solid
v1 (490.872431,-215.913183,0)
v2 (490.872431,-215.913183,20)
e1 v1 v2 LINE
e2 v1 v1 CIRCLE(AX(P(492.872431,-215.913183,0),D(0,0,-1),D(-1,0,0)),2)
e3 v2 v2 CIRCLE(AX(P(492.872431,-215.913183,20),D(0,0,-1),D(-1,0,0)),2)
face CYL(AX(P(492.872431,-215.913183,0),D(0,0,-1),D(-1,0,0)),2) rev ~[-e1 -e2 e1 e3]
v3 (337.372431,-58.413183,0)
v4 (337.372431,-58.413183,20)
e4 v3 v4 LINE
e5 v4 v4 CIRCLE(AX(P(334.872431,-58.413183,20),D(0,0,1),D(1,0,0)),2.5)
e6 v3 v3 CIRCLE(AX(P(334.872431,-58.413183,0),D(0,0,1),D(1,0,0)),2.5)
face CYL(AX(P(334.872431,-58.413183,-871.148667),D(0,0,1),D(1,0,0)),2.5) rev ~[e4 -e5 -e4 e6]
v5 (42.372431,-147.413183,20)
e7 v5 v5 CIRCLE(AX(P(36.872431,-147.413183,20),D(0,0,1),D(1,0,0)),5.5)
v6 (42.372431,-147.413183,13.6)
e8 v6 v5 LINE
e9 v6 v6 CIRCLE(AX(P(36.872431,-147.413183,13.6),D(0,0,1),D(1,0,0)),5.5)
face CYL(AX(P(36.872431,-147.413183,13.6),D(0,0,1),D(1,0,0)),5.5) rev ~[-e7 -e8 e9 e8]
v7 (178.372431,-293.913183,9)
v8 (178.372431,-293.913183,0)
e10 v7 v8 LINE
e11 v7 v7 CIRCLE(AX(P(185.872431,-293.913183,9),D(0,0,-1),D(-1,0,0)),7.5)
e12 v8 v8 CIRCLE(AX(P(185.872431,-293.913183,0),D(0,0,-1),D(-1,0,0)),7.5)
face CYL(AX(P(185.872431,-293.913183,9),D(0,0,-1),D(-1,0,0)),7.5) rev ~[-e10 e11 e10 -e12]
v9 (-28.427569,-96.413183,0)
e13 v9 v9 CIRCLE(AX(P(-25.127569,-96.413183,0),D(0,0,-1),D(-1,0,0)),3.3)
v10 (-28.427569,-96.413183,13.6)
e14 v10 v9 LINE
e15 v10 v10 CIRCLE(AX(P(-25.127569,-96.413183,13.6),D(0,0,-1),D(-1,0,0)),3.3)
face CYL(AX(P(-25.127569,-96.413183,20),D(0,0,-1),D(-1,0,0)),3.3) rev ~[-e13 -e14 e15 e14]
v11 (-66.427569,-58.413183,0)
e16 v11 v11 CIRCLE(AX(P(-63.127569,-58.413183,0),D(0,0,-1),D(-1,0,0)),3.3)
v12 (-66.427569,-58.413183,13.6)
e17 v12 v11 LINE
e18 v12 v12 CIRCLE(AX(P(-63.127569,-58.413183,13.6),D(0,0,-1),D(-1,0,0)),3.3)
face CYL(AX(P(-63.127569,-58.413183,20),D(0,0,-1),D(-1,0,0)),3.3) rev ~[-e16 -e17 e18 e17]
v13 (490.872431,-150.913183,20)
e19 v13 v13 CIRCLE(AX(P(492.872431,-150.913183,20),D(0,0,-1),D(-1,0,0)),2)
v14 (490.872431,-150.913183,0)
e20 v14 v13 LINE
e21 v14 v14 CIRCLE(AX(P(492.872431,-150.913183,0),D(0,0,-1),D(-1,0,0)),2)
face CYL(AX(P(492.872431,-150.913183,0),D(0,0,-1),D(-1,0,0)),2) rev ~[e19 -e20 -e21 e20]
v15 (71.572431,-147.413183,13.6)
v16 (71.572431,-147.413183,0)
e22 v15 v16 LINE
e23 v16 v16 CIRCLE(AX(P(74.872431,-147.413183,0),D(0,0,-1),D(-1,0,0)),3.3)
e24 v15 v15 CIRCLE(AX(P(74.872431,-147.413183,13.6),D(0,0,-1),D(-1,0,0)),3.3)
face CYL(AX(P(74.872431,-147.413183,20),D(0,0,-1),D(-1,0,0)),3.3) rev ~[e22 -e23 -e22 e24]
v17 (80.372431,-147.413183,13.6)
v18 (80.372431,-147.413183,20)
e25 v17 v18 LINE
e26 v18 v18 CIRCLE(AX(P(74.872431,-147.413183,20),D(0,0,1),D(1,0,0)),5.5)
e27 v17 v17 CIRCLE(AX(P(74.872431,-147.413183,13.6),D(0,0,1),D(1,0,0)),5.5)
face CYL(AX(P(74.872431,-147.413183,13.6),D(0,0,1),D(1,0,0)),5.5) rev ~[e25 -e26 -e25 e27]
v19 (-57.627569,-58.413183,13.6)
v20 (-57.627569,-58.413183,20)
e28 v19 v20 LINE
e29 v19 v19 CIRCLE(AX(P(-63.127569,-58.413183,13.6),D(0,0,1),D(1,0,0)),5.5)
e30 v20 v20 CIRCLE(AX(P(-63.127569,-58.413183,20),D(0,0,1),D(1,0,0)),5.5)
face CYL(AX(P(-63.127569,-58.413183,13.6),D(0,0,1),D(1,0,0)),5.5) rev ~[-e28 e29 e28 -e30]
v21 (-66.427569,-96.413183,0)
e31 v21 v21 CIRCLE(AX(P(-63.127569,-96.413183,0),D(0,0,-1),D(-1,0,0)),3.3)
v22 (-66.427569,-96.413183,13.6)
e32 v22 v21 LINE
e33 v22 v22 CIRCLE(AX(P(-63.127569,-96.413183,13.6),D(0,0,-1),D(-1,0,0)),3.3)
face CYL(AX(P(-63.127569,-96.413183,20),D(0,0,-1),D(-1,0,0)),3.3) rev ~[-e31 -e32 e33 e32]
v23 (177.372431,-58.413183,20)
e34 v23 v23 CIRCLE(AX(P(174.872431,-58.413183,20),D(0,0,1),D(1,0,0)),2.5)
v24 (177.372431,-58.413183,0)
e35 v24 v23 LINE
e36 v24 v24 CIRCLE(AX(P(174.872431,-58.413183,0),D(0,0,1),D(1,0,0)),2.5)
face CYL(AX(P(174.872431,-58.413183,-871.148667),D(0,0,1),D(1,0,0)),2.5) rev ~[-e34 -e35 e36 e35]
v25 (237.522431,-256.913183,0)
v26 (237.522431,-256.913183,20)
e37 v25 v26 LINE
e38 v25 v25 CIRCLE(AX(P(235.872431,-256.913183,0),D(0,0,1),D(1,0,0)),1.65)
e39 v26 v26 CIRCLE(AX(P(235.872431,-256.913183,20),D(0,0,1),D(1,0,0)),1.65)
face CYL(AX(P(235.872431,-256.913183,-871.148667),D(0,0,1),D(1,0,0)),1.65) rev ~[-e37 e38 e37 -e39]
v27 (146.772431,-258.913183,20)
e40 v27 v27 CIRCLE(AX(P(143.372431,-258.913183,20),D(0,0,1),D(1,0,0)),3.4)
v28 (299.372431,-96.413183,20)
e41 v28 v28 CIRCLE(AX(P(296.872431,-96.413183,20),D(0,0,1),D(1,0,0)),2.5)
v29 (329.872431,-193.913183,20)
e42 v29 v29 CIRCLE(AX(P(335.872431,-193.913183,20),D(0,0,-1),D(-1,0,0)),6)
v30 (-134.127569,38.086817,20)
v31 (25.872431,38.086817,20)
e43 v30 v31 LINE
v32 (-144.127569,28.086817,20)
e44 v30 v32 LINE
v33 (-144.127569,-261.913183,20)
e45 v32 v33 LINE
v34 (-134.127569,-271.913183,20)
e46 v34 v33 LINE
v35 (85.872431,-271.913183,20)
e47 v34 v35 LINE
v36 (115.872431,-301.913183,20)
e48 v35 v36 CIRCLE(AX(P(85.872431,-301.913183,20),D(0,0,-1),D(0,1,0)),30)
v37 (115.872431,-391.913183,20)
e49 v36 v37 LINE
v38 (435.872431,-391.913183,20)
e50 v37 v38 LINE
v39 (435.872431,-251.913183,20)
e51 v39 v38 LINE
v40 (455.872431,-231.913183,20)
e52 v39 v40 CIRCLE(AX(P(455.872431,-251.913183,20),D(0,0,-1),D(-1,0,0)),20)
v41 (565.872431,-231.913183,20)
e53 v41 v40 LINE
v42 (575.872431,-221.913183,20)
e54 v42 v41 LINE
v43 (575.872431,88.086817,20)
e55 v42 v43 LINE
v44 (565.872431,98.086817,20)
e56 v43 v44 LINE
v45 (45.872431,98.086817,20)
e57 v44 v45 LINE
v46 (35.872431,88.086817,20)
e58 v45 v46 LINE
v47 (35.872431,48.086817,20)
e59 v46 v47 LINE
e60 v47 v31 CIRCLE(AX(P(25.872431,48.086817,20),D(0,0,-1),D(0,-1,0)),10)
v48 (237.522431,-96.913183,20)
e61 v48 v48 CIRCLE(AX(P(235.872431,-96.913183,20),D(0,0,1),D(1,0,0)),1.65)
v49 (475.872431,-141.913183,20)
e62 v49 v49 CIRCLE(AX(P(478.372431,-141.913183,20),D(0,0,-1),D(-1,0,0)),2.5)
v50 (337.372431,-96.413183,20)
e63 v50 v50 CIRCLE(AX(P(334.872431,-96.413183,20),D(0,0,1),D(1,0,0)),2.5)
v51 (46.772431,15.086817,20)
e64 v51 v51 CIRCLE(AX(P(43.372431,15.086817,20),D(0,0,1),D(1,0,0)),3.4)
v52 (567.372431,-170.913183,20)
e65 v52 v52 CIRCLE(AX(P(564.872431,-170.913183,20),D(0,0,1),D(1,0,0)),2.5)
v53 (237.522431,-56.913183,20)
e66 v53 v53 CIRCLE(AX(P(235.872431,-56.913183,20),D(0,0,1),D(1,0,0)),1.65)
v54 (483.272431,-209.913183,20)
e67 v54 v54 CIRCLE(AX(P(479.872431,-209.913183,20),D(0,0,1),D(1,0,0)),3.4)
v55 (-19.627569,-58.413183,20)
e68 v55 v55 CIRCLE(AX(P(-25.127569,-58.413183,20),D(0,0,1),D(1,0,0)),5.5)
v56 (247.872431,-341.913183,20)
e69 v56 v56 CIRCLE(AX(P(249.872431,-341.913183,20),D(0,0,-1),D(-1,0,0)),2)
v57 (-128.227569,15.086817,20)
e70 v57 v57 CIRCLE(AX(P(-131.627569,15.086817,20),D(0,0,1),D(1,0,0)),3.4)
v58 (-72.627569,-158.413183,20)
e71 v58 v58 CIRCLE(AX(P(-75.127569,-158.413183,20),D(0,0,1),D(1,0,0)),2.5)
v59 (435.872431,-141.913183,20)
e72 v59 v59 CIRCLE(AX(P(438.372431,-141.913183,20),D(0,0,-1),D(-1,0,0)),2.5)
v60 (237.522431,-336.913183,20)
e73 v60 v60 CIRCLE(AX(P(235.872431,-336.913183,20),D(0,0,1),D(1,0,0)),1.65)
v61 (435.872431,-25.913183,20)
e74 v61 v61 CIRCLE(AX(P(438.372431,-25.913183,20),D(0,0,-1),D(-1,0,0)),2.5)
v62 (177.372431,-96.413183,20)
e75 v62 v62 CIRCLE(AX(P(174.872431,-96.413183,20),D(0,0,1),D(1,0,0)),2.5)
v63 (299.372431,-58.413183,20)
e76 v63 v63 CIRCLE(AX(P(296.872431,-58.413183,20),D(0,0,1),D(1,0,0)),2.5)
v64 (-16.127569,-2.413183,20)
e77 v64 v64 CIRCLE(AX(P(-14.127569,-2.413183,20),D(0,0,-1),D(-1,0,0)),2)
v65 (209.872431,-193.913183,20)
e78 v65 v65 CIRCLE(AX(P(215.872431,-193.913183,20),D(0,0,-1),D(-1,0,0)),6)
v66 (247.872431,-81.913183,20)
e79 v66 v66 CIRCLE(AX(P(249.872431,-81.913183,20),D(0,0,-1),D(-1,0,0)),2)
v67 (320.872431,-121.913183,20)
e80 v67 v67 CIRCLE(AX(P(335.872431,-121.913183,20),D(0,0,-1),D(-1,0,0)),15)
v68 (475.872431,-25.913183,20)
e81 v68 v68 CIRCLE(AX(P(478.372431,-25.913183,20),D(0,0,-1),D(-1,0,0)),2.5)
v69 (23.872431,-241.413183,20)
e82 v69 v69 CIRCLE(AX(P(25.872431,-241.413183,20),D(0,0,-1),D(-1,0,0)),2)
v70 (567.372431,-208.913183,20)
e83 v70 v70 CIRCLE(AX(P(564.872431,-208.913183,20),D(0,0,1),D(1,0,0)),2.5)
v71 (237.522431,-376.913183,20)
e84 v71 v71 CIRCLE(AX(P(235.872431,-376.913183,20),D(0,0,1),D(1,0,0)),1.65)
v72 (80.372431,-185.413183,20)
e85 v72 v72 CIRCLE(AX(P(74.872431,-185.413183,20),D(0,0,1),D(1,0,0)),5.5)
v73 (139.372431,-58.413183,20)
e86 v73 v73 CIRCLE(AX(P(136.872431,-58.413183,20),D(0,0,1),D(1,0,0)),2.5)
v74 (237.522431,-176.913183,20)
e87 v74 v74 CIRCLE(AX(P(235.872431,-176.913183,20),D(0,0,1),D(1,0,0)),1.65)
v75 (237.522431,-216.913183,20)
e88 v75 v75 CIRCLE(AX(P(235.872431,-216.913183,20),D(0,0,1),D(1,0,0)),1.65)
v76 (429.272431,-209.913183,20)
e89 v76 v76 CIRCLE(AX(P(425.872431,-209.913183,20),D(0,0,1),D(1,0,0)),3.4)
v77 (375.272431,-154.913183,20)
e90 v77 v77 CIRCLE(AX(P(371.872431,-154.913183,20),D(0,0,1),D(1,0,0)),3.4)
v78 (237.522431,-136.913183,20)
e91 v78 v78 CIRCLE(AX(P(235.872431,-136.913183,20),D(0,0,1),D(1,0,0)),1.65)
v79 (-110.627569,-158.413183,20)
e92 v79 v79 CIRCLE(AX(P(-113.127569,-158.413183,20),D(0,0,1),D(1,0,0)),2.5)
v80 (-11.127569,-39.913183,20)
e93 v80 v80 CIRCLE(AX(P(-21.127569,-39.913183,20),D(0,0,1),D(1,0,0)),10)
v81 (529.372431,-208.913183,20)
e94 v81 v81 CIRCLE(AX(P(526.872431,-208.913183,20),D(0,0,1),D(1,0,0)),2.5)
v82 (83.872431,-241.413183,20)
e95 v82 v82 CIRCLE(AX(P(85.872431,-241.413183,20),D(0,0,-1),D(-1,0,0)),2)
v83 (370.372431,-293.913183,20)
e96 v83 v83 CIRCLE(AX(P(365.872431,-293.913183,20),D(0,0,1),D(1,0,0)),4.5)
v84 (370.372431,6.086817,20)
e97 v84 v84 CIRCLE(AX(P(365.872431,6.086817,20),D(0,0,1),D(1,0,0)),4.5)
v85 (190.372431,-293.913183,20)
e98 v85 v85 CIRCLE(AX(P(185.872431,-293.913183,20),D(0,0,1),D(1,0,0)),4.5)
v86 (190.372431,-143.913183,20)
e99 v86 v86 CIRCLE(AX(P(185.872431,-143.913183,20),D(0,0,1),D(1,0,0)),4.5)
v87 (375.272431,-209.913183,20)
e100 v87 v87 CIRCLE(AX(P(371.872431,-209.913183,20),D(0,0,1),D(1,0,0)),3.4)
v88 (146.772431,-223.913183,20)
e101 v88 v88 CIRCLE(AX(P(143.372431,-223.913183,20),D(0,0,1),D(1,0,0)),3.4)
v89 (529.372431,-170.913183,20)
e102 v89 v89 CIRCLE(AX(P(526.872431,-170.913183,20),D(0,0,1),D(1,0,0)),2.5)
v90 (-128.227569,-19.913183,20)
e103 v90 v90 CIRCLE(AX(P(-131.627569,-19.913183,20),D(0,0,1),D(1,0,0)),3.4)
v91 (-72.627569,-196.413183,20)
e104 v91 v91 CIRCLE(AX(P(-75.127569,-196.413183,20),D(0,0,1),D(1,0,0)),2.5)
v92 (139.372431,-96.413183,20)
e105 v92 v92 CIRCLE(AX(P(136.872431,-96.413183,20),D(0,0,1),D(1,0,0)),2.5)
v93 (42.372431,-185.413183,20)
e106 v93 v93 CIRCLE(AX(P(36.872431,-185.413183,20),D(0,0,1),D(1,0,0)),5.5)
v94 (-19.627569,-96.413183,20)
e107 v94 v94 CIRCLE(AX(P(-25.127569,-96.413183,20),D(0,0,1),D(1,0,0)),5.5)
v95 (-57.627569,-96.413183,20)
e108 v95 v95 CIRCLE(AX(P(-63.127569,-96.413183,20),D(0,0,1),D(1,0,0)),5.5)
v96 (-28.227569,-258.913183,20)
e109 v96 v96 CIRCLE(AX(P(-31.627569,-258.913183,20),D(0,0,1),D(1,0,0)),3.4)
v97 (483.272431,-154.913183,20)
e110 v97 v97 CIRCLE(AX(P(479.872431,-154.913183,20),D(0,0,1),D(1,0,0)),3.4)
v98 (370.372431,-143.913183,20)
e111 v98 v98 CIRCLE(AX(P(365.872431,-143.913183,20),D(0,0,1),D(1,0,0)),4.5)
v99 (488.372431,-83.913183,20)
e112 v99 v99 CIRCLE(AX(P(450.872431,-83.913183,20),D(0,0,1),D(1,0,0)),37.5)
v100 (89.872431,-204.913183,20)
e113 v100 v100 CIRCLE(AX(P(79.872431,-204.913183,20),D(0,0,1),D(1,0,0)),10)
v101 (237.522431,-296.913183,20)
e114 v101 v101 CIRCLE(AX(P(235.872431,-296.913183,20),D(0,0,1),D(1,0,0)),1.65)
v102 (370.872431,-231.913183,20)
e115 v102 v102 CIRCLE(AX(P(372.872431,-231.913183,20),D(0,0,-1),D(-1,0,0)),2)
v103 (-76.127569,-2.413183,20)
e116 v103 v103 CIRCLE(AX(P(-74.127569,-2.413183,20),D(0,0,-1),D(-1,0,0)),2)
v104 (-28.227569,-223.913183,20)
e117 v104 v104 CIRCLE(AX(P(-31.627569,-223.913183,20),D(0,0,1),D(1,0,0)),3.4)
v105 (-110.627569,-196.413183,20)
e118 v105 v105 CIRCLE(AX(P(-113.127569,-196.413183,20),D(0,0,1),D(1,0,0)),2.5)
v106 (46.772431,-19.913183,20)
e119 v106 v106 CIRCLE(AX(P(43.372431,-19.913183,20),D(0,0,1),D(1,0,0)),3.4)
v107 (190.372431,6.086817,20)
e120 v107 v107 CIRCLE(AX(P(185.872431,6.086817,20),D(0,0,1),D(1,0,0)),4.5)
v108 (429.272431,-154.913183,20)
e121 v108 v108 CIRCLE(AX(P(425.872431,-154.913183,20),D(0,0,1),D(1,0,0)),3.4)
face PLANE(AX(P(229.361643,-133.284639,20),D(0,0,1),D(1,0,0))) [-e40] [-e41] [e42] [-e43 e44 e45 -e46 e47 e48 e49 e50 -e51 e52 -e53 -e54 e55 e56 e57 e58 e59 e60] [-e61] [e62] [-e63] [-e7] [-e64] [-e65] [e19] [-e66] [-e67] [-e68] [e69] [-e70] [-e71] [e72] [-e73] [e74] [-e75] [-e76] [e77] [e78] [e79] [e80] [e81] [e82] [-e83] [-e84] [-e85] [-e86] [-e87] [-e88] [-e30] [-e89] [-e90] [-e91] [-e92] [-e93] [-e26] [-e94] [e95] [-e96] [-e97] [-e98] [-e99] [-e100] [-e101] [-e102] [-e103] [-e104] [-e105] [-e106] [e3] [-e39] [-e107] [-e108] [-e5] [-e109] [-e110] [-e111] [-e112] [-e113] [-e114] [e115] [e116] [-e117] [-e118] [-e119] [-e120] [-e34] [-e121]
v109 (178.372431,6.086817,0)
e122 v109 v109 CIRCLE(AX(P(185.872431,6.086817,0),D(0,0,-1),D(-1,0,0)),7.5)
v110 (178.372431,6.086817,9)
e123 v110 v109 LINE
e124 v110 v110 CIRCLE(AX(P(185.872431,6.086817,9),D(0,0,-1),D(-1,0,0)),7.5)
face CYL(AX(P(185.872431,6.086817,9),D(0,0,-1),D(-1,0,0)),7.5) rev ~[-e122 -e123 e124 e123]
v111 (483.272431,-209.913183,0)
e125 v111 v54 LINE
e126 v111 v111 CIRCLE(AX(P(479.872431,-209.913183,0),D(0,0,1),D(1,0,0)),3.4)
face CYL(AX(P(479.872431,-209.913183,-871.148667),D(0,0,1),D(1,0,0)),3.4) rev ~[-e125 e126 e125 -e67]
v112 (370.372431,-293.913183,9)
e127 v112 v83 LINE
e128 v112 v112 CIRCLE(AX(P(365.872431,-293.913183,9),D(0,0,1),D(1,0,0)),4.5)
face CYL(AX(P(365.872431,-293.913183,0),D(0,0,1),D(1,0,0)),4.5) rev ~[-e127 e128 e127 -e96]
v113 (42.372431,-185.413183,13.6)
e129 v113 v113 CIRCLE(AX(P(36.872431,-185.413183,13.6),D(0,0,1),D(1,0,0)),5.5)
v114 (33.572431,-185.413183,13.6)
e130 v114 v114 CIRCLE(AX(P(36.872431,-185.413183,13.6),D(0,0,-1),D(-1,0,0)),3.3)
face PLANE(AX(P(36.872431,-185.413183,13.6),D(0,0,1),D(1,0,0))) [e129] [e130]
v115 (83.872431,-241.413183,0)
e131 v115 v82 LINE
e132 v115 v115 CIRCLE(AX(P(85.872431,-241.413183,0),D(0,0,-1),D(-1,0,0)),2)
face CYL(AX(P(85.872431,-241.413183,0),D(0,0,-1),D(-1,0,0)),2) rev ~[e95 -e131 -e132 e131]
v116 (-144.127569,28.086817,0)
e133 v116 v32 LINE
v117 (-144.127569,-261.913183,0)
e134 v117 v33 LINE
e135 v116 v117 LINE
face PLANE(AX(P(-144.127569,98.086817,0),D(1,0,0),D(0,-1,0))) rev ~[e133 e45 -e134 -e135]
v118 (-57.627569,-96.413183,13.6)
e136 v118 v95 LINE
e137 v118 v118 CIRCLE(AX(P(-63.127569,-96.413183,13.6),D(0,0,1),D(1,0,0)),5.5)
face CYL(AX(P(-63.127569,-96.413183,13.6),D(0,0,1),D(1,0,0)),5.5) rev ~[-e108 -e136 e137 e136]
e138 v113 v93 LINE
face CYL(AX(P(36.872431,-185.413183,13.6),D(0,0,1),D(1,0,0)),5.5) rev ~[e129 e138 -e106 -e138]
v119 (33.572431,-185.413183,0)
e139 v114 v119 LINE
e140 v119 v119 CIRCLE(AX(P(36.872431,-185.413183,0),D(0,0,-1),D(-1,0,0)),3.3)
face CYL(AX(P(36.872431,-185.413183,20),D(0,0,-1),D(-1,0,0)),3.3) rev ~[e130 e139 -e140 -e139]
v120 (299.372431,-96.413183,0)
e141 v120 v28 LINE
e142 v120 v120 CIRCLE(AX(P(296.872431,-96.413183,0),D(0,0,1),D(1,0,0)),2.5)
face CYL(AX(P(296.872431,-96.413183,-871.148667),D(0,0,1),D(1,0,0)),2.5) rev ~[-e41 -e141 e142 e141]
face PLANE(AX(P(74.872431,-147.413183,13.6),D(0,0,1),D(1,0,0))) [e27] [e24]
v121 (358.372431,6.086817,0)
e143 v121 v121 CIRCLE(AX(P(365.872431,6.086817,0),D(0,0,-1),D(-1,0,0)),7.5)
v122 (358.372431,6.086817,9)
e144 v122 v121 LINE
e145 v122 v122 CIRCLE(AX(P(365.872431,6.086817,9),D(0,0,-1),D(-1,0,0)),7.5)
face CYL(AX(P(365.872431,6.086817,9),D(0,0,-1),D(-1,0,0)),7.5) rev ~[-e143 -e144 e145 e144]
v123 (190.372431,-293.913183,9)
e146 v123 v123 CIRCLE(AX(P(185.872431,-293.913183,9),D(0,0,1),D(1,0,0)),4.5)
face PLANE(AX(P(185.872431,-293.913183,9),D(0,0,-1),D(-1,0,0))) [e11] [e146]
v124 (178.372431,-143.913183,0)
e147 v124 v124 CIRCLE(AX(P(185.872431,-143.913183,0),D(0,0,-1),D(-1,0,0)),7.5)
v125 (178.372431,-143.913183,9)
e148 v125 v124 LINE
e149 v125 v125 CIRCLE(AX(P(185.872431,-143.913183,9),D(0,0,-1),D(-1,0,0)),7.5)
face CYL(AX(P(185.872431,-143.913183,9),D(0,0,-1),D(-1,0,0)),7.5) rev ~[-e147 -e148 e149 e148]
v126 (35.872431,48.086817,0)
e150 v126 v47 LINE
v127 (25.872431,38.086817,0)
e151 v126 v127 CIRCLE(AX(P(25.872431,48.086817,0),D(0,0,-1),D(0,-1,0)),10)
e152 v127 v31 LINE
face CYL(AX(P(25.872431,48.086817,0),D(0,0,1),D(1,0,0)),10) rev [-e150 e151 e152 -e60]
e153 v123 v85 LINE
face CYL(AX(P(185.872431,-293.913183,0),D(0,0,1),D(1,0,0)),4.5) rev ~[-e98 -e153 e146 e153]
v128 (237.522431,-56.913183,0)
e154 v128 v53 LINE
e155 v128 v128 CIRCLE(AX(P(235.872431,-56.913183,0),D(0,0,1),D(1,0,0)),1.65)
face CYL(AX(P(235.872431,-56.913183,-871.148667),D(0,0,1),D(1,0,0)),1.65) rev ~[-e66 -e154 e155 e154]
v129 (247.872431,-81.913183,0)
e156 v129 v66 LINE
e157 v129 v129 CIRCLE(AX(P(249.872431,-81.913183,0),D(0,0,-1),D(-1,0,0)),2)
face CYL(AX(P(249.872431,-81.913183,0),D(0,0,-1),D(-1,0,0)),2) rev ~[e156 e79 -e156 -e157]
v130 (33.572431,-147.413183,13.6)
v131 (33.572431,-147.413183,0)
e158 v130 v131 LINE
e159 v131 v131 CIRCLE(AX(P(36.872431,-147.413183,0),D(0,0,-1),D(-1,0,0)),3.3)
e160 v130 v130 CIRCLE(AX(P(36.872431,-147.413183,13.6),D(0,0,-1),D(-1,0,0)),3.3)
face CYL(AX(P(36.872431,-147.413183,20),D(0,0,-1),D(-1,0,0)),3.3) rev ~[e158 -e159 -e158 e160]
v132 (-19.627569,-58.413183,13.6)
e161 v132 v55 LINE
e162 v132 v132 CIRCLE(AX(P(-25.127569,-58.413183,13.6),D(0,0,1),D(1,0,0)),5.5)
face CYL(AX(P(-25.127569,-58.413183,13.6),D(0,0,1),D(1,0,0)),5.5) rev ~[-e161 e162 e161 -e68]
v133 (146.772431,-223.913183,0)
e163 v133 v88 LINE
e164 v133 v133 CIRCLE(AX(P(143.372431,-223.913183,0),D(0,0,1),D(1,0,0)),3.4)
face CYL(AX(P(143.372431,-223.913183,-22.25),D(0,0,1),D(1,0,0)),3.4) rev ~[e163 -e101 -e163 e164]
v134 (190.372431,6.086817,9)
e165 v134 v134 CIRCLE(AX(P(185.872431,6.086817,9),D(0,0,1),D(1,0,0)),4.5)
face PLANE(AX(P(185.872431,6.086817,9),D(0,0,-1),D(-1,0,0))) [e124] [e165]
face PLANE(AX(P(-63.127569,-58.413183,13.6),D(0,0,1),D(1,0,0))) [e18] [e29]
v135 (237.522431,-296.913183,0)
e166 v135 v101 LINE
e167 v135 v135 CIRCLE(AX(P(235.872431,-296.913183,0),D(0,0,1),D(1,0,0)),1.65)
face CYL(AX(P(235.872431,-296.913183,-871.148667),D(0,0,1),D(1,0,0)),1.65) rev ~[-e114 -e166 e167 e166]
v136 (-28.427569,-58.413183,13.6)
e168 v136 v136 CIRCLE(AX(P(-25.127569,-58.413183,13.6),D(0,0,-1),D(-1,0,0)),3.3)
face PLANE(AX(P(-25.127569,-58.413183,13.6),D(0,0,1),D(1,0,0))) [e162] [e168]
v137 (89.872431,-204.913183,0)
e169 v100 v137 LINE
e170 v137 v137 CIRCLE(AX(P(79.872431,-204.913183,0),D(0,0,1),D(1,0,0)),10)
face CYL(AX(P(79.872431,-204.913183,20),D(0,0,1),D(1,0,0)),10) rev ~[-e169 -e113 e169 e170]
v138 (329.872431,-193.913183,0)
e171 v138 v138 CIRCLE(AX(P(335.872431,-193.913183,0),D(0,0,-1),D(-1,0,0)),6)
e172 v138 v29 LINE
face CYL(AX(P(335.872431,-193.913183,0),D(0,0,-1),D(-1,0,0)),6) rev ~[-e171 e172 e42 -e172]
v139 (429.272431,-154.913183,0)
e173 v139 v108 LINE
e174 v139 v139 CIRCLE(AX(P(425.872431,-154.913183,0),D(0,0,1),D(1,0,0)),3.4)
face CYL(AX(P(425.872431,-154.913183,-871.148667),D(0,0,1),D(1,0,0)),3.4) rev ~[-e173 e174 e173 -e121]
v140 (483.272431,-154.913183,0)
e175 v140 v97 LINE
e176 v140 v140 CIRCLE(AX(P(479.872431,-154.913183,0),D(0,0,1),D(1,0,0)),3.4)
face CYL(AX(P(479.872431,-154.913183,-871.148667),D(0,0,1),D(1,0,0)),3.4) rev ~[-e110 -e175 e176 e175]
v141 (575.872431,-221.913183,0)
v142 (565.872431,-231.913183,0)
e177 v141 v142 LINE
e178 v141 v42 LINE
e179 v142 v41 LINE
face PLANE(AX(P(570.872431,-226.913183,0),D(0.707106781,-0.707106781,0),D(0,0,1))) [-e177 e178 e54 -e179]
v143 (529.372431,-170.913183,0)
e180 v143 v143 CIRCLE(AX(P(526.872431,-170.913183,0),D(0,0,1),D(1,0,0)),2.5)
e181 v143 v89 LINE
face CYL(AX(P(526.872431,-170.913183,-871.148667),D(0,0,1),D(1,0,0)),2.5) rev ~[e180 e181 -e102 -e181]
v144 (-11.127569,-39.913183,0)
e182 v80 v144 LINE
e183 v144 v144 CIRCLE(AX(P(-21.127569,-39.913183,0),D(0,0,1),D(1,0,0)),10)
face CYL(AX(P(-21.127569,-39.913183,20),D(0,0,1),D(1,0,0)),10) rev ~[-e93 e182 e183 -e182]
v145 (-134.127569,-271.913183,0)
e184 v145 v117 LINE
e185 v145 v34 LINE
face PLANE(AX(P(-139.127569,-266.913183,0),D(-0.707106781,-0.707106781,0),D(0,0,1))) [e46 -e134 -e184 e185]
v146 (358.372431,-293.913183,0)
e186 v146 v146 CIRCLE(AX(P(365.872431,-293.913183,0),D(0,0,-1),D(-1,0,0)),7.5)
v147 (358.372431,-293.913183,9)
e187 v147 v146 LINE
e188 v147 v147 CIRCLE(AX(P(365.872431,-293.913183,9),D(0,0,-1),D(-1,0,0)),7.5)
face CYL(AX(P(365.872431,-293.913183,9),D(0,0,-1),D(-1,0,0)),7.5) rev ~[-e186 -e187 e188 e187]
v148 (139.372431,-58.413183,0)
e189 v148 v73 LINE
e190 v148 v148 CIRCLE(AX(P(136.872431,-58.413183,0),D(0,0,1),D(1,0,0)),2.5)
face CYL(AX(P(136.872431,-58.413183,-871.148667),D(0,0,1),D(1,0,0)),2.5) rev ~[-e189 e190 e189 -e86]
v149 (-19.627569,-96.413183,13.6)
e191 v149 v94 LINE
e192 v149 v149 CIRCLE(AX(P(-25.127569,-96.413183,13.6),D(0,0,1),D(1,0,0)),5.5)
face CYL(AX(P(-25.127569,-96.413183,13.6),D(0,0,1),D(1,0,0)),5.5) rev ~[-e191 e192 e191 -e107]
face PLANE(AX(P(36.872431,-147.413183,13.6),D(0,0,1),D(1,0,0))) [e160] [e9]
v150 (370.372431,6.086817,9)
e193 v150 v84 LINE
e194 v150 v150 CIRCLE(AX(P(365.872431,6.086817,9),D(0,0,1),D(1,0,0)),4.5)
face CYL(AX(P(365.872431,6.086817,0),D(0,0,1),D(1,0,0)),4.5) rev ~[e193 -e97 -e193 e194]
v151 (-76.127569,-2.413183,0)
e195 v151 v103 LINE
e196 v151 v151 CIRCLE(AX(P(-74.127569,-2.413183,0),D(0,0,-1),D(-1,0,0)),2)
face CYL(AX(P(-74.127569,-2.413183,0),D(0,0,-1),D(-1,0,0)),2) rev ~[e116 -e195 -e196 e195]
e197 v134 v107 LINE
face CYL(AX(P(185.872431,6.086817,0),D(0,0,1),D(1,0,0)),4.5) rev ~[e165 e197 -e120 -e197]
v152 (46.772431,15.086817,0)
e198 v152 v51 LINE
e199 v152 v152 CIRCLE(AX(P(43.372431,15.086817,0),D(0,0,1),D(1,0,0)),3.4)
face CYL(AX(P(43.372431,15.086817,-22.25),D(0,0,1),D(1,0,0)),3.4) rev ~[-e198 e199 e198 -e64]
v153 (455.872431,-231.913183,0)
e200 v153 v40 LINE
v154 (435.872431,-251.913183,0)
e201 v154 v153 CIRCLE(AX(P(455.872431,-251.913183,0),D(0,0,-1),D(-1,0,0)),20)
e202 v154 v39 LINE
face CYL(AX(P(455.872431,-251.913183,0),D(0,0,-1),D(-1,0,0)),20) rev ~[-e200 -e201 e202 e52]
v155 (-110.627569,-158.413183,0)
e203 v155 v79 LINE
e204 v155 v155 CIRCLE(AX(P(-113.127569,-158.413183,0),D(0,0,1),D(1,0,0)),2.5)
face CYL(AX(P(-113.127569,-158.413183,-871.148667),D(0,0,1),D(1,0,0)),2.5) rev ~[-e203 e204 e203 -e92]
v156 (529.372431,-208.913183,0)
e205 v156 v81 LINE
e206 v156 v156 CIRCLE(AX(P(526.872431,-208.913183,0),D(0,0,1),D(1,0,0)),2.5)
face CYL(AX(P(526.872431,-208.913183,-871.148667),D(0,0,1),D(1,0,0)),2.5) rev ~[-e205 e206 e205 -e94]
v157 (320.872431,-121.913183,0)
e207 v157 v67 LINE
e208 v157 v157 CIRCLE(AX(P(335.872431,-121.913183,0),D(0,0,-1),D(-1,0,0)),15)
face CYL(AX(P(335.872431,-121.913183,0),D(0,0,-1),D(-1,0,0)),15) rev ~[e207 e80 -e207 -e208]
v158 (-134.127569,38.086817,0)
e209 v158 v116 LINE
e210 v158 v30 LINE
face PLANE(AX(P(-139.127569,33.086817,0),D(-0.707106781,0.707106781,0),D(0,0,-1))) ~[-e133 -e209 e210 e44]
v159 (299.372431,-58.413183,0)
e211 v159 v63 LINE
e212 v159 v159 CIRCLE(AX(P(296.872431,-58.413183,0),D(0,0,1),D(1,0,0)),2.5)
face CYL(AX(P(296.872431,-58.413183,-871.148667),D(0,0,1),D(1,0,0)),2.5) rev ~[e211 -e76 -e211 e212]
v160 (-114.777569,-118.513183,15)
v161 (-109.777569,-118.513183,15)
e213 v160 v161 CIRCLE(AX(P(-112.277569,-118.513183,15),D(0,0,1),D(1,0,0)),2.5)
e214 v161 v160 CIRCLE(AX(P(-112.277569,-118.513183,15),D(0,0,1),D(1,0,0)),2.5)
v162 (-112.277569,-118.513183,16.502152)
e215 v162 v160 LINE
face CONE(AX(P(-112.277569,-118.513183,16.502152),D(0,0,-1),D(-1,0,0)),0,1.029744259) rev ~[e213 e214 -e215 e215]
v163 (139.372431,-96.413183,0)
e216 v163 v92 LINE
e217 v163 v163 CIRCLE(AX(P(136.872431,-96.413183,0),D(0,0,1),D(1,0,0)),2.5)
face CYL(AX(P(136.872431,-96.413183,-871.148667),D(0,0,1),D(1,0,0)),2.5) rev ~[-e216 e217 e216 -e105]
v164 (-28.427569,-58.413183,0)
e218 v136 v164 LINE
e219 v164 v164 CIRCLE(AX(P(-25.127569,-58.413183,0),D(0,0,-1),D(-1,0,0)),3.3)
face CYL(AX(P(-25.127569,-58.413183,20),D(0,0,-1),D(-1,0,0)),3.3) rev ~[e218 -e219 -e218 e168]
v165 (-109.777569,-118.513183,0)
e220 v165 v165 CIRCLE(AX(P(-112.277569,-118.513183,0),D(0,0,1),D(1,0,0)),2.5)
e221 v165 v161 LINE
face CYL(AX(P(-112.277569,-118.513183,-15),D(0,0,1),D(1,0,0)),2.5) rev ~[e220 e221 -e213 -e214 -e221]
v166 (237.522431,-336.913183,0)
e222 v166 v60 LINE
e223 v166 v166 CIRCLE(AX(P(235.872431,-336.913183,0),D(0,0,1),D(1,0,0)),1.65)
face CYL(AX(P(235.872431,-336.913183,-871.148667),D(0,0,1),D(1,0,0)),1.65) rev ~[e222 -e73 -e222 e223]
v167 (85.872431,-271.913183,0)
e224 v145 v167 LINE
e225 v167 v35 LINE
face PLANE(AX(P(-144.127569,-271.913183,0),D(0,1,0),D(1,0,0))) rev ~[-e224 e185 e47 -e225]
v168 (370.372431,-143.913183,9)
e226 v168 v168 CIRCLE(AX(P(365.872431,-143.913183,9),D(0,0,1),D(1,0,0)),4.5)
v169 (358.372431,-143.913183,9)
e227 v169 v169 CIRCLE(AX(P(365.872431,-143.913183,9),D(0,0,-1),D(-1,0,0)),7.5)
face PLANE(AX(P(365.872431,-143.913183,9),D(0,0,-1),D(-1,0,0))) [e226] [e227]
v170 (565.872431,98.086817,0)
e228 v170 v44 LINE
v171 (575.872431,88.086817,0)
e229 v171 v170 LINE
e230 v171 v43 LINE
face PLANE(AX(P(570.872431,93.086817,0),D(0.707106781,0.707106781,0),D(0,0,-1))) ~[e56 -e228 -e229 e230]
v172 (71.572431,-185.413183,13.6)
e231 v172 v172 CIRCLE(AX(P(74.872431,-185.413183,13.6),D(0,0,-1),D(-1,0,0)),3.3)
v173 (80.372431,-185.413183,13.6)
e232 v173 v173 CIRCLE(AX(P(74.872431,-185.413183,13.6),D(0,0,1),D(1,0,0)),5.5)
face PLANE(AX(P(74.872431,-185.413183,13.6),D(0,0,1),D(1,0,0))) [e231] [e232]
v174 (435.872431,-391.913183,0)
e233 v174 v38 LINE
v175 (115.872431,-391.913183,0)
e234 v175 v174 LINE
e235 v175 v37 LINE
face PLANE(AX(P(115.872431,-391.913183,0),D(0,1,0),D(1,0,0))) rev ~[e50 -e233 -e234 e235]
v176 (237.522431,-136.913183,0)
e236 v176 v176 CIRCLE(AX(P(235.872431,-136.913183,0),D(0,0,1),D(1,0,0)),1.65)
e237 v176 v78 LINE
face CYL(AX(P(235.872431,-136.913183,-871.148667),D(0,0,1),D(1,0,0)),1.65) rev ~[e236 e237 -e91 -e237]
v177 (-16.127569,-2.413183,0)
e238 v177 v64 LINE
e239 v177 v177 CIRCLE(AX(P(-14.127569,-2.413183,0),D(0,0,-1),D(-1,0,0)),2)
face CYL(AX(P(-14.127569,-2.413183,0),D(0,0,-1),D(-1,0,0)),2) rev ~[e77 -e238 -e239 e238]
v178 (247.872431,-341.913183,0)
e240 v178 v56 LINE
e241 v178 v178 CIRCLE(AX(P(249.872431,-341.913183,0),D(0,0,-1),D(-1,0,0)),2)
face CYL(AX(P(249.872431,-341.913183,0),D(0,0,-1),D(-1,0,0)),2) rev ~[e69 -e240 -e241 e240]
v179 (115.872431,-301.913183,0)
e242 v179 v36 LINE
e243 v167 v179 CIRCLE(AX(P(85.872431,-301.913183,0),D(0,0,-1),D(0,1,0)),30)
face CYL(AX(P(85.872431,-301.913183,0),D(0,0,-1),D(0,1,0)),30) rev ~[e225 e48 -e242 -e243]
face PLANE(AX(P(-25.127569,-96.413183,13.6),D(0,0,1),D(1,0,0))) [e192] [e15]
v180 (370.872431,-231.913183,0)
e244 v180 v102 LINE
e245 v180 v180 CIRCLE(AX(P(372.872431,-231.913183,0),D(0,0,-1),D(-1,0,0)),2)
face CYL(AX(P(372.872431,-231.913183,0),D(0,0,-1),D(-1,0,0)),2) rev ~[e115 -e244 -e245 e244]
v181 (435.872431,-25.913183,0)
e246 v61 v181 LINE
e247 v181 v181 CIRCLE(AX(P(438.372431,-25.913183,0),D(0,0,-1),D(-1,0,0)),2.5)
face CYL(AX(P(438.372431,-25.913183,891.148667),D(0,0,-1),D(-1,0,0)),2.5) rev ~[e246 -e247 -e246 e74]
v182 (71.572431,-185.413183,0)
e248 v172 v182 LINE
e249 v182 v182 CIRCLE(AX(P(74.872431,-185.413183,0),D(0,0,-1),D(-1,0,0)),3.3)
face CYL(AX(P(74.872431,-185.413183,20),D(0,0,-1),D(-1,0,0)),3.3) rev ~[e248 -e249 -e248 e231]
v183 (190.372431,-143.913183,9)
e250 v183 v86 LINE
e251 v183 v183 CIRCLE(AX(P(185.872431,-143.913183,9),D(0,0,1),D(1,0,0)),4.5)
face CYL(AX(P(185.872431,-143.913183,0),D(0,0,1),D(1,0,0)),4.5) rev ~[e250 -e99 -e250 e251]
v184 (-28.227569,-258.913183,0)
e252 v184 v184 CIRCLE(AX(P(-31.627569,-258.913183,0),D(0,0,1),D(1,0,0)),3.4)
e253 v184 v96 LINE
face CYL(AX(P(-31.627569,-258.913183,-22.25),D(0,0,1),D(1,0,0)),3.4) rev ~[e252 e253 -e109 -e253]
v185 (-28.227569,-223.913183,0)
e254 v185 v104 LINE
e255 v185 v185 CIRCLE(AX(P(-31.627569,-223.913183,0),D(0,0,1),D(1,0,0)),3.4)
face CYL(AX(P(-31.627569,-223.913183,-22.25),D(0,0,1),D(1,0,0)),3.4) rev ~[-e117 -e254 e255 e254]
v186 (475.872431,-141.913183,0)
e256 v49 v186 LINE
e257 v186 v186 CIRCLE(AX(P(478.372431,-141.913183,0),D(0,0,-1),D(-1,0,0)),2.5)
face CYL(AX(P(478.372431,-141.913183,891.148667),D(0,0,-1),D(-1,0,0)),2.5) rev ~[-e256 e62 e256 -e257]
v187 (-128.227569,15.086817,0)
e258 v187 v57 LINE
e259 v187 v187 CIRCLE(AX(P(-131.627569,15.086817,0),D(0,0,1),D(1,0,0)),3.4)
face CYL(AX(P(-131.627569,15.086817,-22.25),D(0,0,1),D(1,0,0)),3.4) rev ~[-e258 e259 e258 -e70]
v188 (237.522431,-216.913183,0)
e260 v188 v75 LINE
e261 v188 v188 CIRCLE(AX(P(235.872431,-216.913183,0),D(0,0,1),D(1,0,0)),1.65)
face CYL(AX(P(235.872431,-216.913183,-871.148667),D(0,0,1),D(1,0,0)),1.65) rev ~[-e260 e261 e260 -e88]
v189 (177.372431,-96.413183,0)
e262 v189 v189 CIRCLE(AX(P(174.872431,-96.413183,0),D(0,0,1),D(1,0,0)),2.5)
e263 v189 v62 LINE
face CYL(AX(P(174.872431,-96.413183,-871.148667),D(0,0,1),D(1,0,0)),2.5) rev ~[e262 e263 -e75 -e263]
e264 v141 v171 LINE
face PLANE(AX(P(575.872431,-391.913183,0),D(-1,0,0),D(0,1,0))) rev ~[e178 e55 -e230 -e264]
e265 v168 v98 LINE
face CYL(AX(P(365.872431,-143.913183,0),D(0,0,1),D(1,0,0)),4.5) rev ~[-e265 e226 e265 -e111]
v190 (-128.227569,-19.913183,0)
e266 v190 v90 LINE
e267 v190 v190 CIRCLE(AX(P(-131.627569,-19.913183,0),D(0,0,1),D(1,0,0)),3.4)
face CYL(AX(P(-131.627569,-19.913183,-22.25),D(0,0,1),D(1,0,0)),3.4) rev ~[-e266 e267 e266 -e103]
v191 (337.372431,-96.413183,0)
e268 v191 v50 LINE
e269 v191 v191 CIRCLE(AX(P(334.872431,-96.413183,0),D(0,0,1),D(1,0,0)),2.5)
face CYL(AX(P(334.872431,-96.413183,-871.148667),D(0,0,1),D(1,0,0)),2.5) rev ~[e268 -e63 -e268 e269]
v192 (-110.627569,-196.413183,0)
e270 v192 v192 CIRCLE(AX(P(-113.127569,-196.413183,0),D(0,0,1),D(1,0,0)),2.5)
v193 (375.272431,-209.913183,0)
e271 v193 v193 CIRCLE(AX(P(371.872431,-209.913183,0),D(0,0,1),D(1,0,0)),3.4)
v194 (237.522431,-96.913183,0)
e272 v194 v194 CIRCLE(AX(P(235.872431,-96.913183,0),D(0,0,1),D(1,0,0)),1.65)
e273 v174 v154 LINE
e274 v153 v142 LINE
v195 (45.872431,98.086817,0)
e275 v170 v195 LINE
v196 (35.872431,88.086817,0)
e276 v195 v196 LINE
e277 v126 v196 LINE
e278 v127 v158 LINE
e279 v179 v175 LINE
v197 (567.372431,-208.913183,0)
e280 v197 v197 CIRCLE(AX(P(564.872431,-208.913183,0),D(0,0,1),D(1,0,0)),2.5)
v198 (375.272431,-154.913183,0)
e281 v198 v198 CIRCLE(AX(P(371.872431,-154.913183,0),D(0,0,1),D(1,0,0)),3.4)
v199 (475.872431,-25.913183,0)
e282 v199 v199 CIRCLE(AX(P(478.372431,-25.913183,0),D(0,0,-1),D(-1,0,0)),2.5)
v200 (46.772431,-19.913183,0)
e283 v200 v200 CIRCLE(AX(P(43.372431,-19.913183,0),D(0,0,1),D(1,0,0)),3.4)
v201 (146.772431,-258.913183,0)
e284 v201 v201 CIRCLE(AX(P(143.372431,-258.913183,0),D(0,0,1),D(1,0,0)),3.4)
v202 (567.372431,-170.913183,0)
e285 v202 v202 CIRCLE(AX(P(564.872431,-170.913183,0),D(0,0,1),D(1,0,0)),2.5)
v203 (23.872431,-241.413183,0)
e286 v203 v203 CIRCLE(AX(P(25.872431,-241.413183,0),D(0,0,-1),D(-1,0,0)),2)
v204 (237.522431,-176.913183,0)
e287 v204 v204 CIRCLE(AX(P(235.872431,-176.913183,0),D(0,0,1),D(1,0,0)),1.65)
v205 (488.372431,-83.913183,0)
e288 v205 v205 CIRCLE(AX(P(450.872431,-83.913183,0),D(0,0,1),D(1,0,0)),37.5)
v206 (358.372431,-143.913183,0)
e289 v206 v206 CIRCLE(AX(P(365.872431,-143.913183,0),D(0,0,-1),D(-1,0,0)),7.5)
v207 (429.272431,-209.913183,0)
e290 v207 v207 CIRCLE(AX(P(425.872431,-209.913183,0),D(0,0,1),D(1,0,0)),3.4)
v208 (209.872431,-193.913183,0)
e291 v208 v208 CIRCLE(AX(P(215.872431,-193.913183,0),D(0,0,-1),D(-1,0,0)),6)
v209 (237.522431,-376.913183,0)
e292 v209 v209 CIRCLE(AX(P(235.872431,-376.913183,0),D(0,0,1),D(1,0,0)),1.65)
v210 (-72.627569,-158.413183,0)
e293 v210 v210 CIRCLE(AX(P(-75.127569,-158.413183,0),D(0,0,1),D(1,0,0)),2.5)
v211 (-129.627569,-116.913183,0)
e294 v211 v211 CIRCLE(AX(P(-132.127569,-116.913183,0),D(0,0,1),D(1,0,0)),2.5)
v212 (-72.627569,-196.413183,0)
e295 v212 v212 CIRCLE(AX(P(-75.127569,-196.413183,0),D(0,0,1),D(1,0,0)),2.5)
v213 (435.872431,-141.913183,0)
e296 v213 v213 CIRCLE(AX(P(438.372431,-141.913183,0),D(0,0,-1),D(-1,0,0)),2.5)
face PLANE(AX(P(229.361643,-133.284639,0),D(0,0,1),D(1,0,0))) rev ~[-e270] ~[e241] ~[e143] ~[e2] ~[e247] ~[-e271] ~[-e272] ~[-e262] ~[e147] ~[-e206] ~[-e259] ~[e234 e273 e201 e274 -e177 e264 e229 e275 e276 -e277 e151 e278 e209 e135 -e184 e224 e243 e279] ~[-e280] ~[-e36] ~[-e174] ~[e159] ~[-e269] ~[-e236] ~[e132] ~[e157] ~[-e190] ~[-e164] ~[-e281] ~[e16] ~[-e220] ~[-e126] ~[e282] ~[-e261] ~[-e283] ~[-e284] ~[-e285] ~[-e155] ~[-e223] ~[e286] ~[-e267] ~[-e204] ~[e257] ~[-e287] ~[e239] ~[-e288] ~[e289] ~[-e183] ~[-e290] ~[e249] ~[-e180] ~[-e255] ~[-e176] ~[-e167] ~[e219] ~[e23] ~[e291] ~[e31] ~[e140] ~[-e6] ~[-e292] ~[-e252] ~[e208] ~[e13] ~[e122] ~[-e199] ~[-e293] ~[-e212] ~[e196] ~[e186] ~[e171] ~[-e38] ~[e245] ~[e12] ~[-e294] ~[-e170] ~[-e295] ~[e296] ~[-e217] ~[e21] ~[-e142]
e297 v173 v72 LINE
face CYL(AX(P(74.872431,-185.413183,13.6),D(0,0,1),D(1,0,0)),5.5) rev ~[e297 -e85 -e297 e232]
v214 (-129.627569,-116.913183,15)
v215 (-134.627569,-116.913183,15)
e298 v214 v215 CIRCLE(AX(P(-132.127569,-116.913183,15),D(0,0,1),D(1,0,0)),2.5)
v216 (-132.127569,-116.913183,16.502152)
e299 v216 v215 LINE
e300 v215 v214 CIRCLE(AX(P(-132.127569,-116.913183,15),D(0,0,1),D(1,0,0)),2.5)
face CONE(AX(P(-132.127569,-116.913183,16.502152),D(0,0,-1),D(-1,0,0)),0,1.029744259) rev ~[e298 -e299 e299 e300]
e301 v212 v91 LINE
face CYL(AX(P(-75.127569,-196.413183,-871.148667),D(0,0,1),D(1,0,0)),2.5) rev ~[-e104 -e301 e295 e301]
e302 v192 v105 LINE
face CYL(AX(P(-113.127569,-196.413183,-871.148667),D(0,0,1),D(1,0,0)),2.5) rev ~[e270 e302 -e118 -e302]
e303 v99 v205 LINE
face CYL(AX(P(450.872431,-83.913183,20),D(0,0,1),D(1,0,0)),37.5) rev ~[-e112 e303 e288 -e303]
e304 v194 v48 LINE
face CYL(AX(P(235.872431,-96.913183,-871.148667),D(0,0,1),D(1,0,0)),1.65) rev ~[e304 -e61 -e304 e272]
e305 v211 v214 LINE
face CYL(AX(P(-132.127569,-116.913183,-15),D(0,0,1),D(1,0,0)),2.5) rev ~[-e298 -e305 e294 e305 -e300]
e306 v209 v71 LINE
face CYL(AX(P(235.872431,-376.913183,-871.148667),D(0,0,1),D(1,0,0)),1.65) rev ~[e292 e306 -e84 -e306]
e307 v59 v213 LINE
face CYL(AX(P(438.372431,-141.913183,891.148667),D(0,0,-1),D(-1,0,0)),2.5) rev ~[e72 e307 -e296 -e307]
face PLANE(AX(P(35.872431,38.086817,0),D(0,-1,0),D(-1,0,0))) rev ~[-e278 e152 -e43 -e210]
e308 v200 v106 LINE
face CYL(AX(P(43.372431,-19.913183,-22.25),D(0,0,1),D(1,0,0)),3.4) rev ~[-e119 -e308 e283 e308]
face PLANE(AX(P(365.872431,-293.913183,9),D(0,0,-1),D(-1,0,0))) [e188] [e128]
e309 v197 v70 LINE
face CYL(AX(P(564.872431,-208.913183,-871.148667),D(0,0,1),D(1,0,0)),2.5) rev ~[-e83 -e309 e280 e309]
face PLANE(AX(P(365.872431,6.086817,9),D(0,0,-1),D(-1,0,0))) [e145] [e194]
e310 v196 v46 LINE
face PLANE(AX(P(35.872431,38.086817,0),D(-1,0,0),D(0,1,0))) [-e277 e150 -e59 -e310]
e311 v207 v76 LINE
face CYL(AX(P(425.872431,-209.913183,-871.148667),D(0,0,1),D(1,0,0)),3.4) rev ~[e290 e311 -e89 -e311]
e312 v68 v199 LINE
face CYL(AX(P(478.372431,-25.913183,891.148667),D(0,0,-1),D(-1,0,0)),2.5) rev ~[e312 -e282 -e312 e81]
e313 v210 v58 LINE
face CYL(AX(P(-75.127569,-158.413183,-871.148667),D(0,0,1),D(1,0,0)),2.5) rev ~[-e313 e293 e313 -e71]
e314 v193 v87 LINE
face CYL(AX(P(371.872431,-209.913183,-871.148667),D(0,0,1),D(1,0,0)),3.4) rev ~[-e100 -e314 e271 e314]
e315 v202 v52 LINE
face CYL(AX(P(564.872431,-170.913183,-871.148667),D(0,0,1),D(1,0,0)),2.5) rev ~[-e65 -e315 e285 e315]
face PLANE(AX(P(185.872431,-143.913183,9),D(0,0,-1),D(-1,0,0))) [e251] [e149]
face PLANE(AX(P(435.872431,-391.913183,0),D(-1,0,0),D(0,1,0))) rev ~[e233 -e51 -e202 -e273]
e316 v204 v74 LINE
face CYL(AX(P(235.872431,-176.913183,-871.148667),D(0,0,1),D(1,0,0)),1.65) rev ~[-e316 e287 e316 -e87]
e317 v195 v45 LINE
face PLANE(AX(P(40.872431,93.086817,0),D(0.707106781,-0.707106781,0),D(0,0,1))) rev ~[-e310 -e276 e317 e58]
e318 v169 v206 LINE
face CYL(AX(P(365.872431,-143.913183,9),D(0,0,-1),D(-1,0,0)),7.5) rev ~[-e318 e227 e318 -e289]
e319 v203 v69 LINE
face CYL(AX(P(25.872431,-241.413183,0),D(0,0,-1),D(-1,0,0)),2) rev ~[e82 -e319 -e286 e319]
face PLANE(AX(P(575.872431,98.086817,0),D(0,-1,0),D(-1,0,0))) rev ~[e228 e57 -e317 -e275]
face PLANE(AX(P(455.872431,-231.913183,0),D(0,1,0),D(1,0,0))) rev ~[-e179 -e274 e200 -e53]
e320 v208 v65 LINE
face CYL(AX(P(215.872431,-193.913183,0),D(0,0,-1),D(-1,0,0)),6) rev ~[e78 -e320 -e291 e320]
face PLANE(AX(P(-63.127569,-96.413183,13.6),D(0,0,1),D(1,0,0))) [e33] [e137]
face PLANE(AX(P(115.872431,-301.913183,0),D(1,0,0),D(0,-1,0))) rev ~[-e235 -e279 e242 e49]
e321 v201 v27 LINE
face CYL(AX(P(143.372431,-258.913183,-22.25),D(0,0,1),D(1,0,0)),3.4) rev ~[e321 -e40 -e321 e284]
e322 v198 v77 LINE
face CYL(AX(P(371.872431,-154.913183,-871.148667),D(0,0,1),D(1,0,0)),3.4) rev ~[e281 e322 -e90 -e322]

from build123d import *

# Parameters (mm, degrees)
BOSS_EXTRUDE3_DEPTH                                  = 20
CHAMFER1_SIZE                                        = 10
CUT_EXTRUDE3_DEPTH                                   = 697.867993238
CHAMFER2_SIZE                                        = 10
SKETCH20_R                                           = 15
CUT_EXTRUDE5_DEPTH                                   = 697.867993238
M6_TAPPED_HOLE1_D                                    = 5
M8_TAPPED_HOLE1_D                                    = 6.8
M4_TAPPED_HOLE1_D                                    = 3.3
SKETCH30_R                                           = 37.5
CUT_EXTRUDE6_DEPTH                                   = 697.867993238
HOLE_SIZE_PER_SOCKET_HEAD_CAP_SCREW_TYPE_D           = 9
HOLE_SIZE_PER_SOCKET_HEAD_CAP_SCREW_TYPE_CBORE_D     = 15
HOLE_SIZE_PER_SOCKET_HEAD_CAP_SCREW_TYPE_CBORE_DEPTH = 9
SKETCH34_R                                           = 6
CUT_EXTRUDE7_DEPTH                                   = 697.867993238
M6_TAPPED_HOLE2_D                                    = 5
SKETCH37_W                                           = 180
SKETCH37_H                                           = 60
CUT_EXTRUDE8_DEPTH                                   = 697.867993238
LPATTERN1_COUNT                                      = 9
LPATTERN1_PITCH                                      = 40
CBORE_FOR_M6_HEX_SOCKET_HEAD_CAP_SCREW1_D            = 6.6
CBORE_FOR_M6_HEX_SOCKET_HEAD_CAP_SCREW1_CBORE_D      = 11
CBORE_FOR_M6_HEX_SOCKET_HEAD_CAP_SCREW1_CBORE_DEPTH  = 6.4
CHAMFER3_SIZE                                        = 10
FILLET1_R                                            = 10
SKETCH40_R                                           = 10
CUT_EXTRUDE9_DEPTH                                   = 697.867993238
M8_TAPPED_HOLE2_D                                    = 6.8
M8_TAPPED_HOLE2_DEPTH                                = 22.25
M8_TAPPED_HOLE2_TIP                                  = 2.042926105
SKETCH43_R                                           = 2
CUT_EXTRUDE10_DEPTH                                  = 697.867993238
SKETCH44_R                                           = 2
CUT_EXTRUDE11_DEPTH                                  = 697.867993238
SKETCH45_R                                           = 2
CUT_EXTRUDE12_DEPTH                                  = 697.867993238
M6_TAPPED_HOLE3_D                                    = 5
M6_TAPPED_HOLE3_DEPTH                                = 15
M6_TAPPED_HOLE3_TIP                                  = 1.502151548


with BuildPart() as part:
    # Sketch2 → Boss-Extrude3 (new body)
    with BuildSketch(Plane.XY):
        with BuildLine():
            Line((-144.12756851, -271.913182542), (85.87243149, -271.913182542))
            ThreePointArc((85.87243149, -271.913182542), (107.085634925, -280.699979106), (115.87243149, -301.913182542))
            Line((115.87243149, -301.913182542), (115.87243149, -391.913182542))
            Line((115.87243149, -391.913182542), (575.87243149, -391.913182542))
            Line((575.87243149, -391.913182542), (575.87243149, 98.086817458))
            Line((575.87243149, 98.086817458), (-144.12756851, 98.086817458))
            Line((-144.12756851, 98.086817458), (-144.12756851, -271.913182542))
        make_face()
    extrude(amount=BOSS_EXTRUDE3_DEPTH)

    # Chamfer1
    chamfer1_edges = [part.edges().sort_by_distance(p)[0] for p in [
        (-144.12756851, -271.913182542, 10),
        (-144.12756851, 98.086817458, 10),
        (575.87243149, 98.086817458, 10),
    ]]
    chamfer(chamfer1_edges, length=CHAMFER1_SIZE)

    # Sketch6 → Cut-Extrude3 (cut, through all)
    with BuildSketch(Plane(origin=(0, 0, 0), x_dir=(-1, 0, 0), z_dir=(0, 0, -1))):
        with BuildLine():
            Line((-575.87243149, -391.913182542), (-435.87243149, -391.913182542))
            Line((-435.87243149, -391.913182542), (-435.87243149, -251.913182542))
            ThreePointArc((-435.87243149, -251.913182542), (-441.730295866, -237.771046918), (-455.87243149, -231.913182542))
            Line((-455.87243149, -231.913182542), (-575.87243149, -231.913182542))
            Line((-575.87243149, -231.913182542), (-575.87243149, -391.913182542))
        make_face()
    extrude(amount=-CUT_EXTRUDE3_DEPTH, mode=Mode.SUBTRACT)

    # Chamfer2
    chamfer2_edges = [part.edges().sort_by_distance(p)[0] for p in [
        (575.87243149, -231.913182542, 10),
    ]]
    chamfer(chamfer2_edges, length=CHAMFER2_SIZE)

    # Sketch20 → Cut-Extrude5 (cut, through all)
    with BuildSketch(Plane(origin=(0, 0, 0), x_dir=(-1, 0, 0), z_dir=(0, 0, -1))):
        with Locations((-335.87243149, -121.913182542)):
            Circle(SKETCH20_R)
    extrude(amount=-CUT_EXTRUDE5_DEPTH, mode=Mode.SUBTRACT)

    # M6 Tapped Hole1 (through all)
    with Locations(Plane.XY.offset(20)):
        with Locations((438.37243149, -25.913182542), (478.37243149, -25.913182542), (478.37243149, -141.913182542), (438.37243149, -141.913182542)):
            Hole(M6_TAPPED_HOLE1_D / 2)

    # M8 Tapped Hole1 (through all)
    with Locations(Plane(origin=(0, 0, 0), x_dir=(-1, 0, 0), z_dir=(0, 0, -1))):
        with Locations((-425.87243149, -209.913182542), (-425.87243149, -154.913182542), (-371.87243149, -154.913182542), (-371.87243149, -209.913182542), (-479.87243149, -154.913182542), (-479.87243149, -209.913182542)):
            Hole(M8_TAPPED_HOLE1_D / 2)

    # M4 Tapped Hole1 (through all)
    with Locations(Plane(origin=(0, 0, 0), x_dir=(-1, 0, 0), z_dir=(0, 0, -1))):
        with Locations((-235.87243149, -376.913182542)):
            m4_tapped_hole1 = Hole(M4_TAPPED_HOLE1_D / 2)

    # Sketch30 → Cut-Extrude6 (cut, through all)
    with BuildSketch(Plane.XY.offset(20)):
        with Locations((450.87243149, -83.913182542)):
            Circle(SKETCH30_R)
    extrude(amount=-CUT_EXTRUDE6_DEPTH, mode=Mode.SUBTRACT)

    # Hole size per socket head cap screw type 1 (through all)
    with Locations(Plane(origin=(0, 0, 0), x_dir=(-1, 0, 0), z_dir=(0, 0, -1))):
        with Locations((-185.87243149, 6.086817458), (-365.87243149, 6.086817458), (-365.87243149, -143.913182542), (-185.87243149, -143.913182542), (-365.87243149, -293.913182542), (-185.87243149, -293.913182542)):
            CounterBoreHole(HOLE_SIZE_PER_SOCKET_HEAD_CAP_SCREW_TYPE_D / 2, HOLE_SIZE_PER_SOCKET_HEAD_CAP_SCREW_TYPE_CBORE_D / 2, HOLE_SIZE_PER_SOCKET_HEAD_CAP_SCREW_TYPE_CBORE_DEPTH)

    # Sketch34 → Cut-Extrude7 (cut, through all)
    with BuildSketch(Plane(origin=(0, 0, 0), x_dir=(-1, 0, 0), z_dir=(0, 0, -1))):
        with Locations((-335.87243149, -193.913182542)):
            Circle(SKETCH34_R)
        with Locations((-215.87243149, -193.913182542)):
            Circle(SKETCH34_R)
    extrude(amount=-CUT_EXTRUDE7_DEPTH, mode=Mode.SUBTRACT)

    # M6 Tapped Hole2 (through all)
    with Locations(Plane(origin=(0, 0, 0), x_dir=(-1, 0, 0), z_dir=(0, 0, -1))):
        with Locations((-564.87243149, -170.913182542), (-526.87243149, -170.913182542), (-526.87243149, -208.913182542), (-564.87243149, -208.913182542), (-334.87243149, -58.413182542), (-296.87243149, -58.413182542), (-296.87243149, -96.413182542), (-334.87243149, -96.413182542), (-174.87243149, -58.413182542), (-136.87243149, -58.413182542), (-136.87243149, -96.413182542), (-174.87243149, -96.413182542), (75.12756851, -158.413182542), (113.12756851, -158.413182542), (113.12756851, -196.413182542), (75.12756851, -196.413182542)):
            Hole(M6_TAPPED_HOLE2_D / 2)

    # Sketch37 → Cut-Extrude8 (cut, through all)
    with BuildSketch(Plane(origin=(0, 0, 0), x_dir=(-1, 0, 0), z_dir=(0, 0, -1))):
        with Locations((54.12756851, 68.086817458)):
            Rectangle(SKETCH37_W, SKETCH37_H)
    extrude(amount=-CUT_EXTRUDE8_DEPTH, mode=Mode.SUBTRACT)

    # LPattern1: M4 Tapped Hole1 ×9
    with Locations(*[(0, i * LPATTERN1_PITCH, 0) for i in range(1, LPATTERN1_COUNT)]):
        add(m4_tapped_hole1, mode=Mode.SUBTRACT)

    # CBORE for M6 Hex Socket Head Cap Screw1 (through all)
    with Locations(Plane.XY.offset(20)):
        with Locations((36.87243149, -147.413182542), (74.87243149, -147.413182542), (74.87243149, -185.413182542), (36.87243149, -185.413182542), (-25.12756851, -58.413182542), (-63.12756851, -58.413182542), (-63.12756851, -96.413182542), (-25.12756851, -96.413182542)):
            CounterBoreHole(CBORE_FOR_M6_HEX_SOCKET_HEAD_CAP_SCREW1_D / 2, CBORE_FOR_M6_HEX_SOCKET_HEAD_CAP_SCREW1_CBORE_D / 2, CBORE_FOR_M6_HEX_SOCKET_HEAD_CAP_SCREW1_CBORE_DEPTH)

    # Chamfer3
    chamfer3_edges = [part.edges().sort_by_distance(p)[0] for p in [
        (35.87243149, 98.086817458, 10),
        (-144.12756851, 38.086817458, 10),
    ]]
    chamfer(chamfer3_edges, length=CHAMFER3_SIZE)

    # Fillet1
    fillet1_edges = [part.edges().sort_by_distance(p)[0] for p in [
        (35.87243149, 38.086817458, 10),
    ]]
    fillet(fillet1_edges, radius=FILLET1_R)

    # Sketch40 → Cut-Extrude9 (cut, through all)
    with BuildSketch(Plane.XY.offset(20)):
        with Locations((79.87243149, -204.913182542)):
            Circle(SKETCH40_R)
        with Locations((-21.12756851, -39.913182542)):
            Circle(SKETCH40_R)
    extrude(amount=-CUT_EXTRUDE9_DEPTH, mode=Mode.SUBTRACT)

    # M8 Tapped Hole2
    with Locations(Plane(origin=(0, 0, 0), x_dir=(-1, 0, 0), z_dir=(0, 0, -1))):
        with Locations((-43.37243149, 15.086817458), (-43.37243149, -19.913182542), (131.62756851, 15.086817458), (-143.37243149, -223.913182542), (-143.37243149, -258.913182542), (31.62756851, -223.913182542), (31.62756851, -258.913182542), (131.62756851, -19.913182542)):
            Hole(M8_TAPPED_HOLE2_D / 2, depth=M8_TAPPED_HOLE2_DEPTH)
            with Locations((0, 0, -(M8_TAPPED_HOLE2_DEPTH + M8_TAPPED_HOLE2_TIP / 2))):  # 118° drill point
                Cone(0, M8_TAPPED_HOLE2_D / 2, M8_TAPPED_HOLE2_TIP, mode=Mode.SUBTRACT)

    # Sketch43 → Cut-Extrude10 (cut, through all)
    with BuildSketch(Plane(origin=(0, 0, 0), x_dir=(-1, 0, 0), z_dir=(0, 0, -1))):
        with Locations((14.12756851, -2.413182542)):
            Circle(SKETCH43_R)
        with Locations((74.12756851, -2.413182542)):
            Circle(SKETCH43_R)
        with Locations((-85.87243149, -241.413182542)):
            Circle(SKETCH43_R)
        with Locations((-25.87243149, -241.413182542)):
            Circle(SKETCH43_R)
    extrude(amount=-CUT_EXTRUDE10_DEPTH, mode=Mode.SUBTRACT)

    # Sketch44 → Cut-Extrude11 (cut, through all)
    with BuildSketch(Plane(origin=(0, 0, 0), x_dir=(-1, 0, 0), z_dir=(0, 0, -1))):
        with Locations((-249.87243149, -341.913182542)):
            Circle(SKETCH44_R)
        with Locations((-249.87243149, -81.913182542)):
            Circle(SKETCH44_R)
    extrude(amount=-CUT_EXTRUDE11_DEPTH, mode=Mode.SUBTRACT)

    # Sketch45 → Cut-Extrude12 (cut, through all)
    with BuildSketch(Plane(origin=(0, 0, 0), x_dir=(-1, 0, 0), z_dir=(0, 0, -1))):
        with Locations((-492.87243149, -150.913182542)):
            Circle(SKETCH45_R)
        with Locations((-492.87243149, -215.913182542)):
            Circle(SKETCH45_R)
        with Locations((-372.87243149, -231.913182542)):
            Circle(SKETCH45_R)
    extrude(amount=-CUT_EXTRUDE12_DEPTH, mode=Mode.SUBTRACT)

    # M6 Tapped Hole3
    with Locations(Plane(origin=(0, 0, 0), x_dir=(-1, 0, 0), z_dir=(0, 0, -1))):
        with Locations((112.27756851, -118.513182542), (132.12756851, -116.913182542)):
            Hole(M6_TAPPED_HOLE3_D / 2, depth=M6_TAPPED_HOLE3_DEPTH)
            with Locations((0, 0, -(M6_TAPPED_HOLE3_DEPTH + M6_TAPPED_HOLE3_TIP / 2))):  # 118° drill point
                Cone(0, M6_TAPPED_HOLE3_D / 2, M6_TAPPED_HOLE3_TIP, mode=Mode.SUBTRACT)


solid = part.part
